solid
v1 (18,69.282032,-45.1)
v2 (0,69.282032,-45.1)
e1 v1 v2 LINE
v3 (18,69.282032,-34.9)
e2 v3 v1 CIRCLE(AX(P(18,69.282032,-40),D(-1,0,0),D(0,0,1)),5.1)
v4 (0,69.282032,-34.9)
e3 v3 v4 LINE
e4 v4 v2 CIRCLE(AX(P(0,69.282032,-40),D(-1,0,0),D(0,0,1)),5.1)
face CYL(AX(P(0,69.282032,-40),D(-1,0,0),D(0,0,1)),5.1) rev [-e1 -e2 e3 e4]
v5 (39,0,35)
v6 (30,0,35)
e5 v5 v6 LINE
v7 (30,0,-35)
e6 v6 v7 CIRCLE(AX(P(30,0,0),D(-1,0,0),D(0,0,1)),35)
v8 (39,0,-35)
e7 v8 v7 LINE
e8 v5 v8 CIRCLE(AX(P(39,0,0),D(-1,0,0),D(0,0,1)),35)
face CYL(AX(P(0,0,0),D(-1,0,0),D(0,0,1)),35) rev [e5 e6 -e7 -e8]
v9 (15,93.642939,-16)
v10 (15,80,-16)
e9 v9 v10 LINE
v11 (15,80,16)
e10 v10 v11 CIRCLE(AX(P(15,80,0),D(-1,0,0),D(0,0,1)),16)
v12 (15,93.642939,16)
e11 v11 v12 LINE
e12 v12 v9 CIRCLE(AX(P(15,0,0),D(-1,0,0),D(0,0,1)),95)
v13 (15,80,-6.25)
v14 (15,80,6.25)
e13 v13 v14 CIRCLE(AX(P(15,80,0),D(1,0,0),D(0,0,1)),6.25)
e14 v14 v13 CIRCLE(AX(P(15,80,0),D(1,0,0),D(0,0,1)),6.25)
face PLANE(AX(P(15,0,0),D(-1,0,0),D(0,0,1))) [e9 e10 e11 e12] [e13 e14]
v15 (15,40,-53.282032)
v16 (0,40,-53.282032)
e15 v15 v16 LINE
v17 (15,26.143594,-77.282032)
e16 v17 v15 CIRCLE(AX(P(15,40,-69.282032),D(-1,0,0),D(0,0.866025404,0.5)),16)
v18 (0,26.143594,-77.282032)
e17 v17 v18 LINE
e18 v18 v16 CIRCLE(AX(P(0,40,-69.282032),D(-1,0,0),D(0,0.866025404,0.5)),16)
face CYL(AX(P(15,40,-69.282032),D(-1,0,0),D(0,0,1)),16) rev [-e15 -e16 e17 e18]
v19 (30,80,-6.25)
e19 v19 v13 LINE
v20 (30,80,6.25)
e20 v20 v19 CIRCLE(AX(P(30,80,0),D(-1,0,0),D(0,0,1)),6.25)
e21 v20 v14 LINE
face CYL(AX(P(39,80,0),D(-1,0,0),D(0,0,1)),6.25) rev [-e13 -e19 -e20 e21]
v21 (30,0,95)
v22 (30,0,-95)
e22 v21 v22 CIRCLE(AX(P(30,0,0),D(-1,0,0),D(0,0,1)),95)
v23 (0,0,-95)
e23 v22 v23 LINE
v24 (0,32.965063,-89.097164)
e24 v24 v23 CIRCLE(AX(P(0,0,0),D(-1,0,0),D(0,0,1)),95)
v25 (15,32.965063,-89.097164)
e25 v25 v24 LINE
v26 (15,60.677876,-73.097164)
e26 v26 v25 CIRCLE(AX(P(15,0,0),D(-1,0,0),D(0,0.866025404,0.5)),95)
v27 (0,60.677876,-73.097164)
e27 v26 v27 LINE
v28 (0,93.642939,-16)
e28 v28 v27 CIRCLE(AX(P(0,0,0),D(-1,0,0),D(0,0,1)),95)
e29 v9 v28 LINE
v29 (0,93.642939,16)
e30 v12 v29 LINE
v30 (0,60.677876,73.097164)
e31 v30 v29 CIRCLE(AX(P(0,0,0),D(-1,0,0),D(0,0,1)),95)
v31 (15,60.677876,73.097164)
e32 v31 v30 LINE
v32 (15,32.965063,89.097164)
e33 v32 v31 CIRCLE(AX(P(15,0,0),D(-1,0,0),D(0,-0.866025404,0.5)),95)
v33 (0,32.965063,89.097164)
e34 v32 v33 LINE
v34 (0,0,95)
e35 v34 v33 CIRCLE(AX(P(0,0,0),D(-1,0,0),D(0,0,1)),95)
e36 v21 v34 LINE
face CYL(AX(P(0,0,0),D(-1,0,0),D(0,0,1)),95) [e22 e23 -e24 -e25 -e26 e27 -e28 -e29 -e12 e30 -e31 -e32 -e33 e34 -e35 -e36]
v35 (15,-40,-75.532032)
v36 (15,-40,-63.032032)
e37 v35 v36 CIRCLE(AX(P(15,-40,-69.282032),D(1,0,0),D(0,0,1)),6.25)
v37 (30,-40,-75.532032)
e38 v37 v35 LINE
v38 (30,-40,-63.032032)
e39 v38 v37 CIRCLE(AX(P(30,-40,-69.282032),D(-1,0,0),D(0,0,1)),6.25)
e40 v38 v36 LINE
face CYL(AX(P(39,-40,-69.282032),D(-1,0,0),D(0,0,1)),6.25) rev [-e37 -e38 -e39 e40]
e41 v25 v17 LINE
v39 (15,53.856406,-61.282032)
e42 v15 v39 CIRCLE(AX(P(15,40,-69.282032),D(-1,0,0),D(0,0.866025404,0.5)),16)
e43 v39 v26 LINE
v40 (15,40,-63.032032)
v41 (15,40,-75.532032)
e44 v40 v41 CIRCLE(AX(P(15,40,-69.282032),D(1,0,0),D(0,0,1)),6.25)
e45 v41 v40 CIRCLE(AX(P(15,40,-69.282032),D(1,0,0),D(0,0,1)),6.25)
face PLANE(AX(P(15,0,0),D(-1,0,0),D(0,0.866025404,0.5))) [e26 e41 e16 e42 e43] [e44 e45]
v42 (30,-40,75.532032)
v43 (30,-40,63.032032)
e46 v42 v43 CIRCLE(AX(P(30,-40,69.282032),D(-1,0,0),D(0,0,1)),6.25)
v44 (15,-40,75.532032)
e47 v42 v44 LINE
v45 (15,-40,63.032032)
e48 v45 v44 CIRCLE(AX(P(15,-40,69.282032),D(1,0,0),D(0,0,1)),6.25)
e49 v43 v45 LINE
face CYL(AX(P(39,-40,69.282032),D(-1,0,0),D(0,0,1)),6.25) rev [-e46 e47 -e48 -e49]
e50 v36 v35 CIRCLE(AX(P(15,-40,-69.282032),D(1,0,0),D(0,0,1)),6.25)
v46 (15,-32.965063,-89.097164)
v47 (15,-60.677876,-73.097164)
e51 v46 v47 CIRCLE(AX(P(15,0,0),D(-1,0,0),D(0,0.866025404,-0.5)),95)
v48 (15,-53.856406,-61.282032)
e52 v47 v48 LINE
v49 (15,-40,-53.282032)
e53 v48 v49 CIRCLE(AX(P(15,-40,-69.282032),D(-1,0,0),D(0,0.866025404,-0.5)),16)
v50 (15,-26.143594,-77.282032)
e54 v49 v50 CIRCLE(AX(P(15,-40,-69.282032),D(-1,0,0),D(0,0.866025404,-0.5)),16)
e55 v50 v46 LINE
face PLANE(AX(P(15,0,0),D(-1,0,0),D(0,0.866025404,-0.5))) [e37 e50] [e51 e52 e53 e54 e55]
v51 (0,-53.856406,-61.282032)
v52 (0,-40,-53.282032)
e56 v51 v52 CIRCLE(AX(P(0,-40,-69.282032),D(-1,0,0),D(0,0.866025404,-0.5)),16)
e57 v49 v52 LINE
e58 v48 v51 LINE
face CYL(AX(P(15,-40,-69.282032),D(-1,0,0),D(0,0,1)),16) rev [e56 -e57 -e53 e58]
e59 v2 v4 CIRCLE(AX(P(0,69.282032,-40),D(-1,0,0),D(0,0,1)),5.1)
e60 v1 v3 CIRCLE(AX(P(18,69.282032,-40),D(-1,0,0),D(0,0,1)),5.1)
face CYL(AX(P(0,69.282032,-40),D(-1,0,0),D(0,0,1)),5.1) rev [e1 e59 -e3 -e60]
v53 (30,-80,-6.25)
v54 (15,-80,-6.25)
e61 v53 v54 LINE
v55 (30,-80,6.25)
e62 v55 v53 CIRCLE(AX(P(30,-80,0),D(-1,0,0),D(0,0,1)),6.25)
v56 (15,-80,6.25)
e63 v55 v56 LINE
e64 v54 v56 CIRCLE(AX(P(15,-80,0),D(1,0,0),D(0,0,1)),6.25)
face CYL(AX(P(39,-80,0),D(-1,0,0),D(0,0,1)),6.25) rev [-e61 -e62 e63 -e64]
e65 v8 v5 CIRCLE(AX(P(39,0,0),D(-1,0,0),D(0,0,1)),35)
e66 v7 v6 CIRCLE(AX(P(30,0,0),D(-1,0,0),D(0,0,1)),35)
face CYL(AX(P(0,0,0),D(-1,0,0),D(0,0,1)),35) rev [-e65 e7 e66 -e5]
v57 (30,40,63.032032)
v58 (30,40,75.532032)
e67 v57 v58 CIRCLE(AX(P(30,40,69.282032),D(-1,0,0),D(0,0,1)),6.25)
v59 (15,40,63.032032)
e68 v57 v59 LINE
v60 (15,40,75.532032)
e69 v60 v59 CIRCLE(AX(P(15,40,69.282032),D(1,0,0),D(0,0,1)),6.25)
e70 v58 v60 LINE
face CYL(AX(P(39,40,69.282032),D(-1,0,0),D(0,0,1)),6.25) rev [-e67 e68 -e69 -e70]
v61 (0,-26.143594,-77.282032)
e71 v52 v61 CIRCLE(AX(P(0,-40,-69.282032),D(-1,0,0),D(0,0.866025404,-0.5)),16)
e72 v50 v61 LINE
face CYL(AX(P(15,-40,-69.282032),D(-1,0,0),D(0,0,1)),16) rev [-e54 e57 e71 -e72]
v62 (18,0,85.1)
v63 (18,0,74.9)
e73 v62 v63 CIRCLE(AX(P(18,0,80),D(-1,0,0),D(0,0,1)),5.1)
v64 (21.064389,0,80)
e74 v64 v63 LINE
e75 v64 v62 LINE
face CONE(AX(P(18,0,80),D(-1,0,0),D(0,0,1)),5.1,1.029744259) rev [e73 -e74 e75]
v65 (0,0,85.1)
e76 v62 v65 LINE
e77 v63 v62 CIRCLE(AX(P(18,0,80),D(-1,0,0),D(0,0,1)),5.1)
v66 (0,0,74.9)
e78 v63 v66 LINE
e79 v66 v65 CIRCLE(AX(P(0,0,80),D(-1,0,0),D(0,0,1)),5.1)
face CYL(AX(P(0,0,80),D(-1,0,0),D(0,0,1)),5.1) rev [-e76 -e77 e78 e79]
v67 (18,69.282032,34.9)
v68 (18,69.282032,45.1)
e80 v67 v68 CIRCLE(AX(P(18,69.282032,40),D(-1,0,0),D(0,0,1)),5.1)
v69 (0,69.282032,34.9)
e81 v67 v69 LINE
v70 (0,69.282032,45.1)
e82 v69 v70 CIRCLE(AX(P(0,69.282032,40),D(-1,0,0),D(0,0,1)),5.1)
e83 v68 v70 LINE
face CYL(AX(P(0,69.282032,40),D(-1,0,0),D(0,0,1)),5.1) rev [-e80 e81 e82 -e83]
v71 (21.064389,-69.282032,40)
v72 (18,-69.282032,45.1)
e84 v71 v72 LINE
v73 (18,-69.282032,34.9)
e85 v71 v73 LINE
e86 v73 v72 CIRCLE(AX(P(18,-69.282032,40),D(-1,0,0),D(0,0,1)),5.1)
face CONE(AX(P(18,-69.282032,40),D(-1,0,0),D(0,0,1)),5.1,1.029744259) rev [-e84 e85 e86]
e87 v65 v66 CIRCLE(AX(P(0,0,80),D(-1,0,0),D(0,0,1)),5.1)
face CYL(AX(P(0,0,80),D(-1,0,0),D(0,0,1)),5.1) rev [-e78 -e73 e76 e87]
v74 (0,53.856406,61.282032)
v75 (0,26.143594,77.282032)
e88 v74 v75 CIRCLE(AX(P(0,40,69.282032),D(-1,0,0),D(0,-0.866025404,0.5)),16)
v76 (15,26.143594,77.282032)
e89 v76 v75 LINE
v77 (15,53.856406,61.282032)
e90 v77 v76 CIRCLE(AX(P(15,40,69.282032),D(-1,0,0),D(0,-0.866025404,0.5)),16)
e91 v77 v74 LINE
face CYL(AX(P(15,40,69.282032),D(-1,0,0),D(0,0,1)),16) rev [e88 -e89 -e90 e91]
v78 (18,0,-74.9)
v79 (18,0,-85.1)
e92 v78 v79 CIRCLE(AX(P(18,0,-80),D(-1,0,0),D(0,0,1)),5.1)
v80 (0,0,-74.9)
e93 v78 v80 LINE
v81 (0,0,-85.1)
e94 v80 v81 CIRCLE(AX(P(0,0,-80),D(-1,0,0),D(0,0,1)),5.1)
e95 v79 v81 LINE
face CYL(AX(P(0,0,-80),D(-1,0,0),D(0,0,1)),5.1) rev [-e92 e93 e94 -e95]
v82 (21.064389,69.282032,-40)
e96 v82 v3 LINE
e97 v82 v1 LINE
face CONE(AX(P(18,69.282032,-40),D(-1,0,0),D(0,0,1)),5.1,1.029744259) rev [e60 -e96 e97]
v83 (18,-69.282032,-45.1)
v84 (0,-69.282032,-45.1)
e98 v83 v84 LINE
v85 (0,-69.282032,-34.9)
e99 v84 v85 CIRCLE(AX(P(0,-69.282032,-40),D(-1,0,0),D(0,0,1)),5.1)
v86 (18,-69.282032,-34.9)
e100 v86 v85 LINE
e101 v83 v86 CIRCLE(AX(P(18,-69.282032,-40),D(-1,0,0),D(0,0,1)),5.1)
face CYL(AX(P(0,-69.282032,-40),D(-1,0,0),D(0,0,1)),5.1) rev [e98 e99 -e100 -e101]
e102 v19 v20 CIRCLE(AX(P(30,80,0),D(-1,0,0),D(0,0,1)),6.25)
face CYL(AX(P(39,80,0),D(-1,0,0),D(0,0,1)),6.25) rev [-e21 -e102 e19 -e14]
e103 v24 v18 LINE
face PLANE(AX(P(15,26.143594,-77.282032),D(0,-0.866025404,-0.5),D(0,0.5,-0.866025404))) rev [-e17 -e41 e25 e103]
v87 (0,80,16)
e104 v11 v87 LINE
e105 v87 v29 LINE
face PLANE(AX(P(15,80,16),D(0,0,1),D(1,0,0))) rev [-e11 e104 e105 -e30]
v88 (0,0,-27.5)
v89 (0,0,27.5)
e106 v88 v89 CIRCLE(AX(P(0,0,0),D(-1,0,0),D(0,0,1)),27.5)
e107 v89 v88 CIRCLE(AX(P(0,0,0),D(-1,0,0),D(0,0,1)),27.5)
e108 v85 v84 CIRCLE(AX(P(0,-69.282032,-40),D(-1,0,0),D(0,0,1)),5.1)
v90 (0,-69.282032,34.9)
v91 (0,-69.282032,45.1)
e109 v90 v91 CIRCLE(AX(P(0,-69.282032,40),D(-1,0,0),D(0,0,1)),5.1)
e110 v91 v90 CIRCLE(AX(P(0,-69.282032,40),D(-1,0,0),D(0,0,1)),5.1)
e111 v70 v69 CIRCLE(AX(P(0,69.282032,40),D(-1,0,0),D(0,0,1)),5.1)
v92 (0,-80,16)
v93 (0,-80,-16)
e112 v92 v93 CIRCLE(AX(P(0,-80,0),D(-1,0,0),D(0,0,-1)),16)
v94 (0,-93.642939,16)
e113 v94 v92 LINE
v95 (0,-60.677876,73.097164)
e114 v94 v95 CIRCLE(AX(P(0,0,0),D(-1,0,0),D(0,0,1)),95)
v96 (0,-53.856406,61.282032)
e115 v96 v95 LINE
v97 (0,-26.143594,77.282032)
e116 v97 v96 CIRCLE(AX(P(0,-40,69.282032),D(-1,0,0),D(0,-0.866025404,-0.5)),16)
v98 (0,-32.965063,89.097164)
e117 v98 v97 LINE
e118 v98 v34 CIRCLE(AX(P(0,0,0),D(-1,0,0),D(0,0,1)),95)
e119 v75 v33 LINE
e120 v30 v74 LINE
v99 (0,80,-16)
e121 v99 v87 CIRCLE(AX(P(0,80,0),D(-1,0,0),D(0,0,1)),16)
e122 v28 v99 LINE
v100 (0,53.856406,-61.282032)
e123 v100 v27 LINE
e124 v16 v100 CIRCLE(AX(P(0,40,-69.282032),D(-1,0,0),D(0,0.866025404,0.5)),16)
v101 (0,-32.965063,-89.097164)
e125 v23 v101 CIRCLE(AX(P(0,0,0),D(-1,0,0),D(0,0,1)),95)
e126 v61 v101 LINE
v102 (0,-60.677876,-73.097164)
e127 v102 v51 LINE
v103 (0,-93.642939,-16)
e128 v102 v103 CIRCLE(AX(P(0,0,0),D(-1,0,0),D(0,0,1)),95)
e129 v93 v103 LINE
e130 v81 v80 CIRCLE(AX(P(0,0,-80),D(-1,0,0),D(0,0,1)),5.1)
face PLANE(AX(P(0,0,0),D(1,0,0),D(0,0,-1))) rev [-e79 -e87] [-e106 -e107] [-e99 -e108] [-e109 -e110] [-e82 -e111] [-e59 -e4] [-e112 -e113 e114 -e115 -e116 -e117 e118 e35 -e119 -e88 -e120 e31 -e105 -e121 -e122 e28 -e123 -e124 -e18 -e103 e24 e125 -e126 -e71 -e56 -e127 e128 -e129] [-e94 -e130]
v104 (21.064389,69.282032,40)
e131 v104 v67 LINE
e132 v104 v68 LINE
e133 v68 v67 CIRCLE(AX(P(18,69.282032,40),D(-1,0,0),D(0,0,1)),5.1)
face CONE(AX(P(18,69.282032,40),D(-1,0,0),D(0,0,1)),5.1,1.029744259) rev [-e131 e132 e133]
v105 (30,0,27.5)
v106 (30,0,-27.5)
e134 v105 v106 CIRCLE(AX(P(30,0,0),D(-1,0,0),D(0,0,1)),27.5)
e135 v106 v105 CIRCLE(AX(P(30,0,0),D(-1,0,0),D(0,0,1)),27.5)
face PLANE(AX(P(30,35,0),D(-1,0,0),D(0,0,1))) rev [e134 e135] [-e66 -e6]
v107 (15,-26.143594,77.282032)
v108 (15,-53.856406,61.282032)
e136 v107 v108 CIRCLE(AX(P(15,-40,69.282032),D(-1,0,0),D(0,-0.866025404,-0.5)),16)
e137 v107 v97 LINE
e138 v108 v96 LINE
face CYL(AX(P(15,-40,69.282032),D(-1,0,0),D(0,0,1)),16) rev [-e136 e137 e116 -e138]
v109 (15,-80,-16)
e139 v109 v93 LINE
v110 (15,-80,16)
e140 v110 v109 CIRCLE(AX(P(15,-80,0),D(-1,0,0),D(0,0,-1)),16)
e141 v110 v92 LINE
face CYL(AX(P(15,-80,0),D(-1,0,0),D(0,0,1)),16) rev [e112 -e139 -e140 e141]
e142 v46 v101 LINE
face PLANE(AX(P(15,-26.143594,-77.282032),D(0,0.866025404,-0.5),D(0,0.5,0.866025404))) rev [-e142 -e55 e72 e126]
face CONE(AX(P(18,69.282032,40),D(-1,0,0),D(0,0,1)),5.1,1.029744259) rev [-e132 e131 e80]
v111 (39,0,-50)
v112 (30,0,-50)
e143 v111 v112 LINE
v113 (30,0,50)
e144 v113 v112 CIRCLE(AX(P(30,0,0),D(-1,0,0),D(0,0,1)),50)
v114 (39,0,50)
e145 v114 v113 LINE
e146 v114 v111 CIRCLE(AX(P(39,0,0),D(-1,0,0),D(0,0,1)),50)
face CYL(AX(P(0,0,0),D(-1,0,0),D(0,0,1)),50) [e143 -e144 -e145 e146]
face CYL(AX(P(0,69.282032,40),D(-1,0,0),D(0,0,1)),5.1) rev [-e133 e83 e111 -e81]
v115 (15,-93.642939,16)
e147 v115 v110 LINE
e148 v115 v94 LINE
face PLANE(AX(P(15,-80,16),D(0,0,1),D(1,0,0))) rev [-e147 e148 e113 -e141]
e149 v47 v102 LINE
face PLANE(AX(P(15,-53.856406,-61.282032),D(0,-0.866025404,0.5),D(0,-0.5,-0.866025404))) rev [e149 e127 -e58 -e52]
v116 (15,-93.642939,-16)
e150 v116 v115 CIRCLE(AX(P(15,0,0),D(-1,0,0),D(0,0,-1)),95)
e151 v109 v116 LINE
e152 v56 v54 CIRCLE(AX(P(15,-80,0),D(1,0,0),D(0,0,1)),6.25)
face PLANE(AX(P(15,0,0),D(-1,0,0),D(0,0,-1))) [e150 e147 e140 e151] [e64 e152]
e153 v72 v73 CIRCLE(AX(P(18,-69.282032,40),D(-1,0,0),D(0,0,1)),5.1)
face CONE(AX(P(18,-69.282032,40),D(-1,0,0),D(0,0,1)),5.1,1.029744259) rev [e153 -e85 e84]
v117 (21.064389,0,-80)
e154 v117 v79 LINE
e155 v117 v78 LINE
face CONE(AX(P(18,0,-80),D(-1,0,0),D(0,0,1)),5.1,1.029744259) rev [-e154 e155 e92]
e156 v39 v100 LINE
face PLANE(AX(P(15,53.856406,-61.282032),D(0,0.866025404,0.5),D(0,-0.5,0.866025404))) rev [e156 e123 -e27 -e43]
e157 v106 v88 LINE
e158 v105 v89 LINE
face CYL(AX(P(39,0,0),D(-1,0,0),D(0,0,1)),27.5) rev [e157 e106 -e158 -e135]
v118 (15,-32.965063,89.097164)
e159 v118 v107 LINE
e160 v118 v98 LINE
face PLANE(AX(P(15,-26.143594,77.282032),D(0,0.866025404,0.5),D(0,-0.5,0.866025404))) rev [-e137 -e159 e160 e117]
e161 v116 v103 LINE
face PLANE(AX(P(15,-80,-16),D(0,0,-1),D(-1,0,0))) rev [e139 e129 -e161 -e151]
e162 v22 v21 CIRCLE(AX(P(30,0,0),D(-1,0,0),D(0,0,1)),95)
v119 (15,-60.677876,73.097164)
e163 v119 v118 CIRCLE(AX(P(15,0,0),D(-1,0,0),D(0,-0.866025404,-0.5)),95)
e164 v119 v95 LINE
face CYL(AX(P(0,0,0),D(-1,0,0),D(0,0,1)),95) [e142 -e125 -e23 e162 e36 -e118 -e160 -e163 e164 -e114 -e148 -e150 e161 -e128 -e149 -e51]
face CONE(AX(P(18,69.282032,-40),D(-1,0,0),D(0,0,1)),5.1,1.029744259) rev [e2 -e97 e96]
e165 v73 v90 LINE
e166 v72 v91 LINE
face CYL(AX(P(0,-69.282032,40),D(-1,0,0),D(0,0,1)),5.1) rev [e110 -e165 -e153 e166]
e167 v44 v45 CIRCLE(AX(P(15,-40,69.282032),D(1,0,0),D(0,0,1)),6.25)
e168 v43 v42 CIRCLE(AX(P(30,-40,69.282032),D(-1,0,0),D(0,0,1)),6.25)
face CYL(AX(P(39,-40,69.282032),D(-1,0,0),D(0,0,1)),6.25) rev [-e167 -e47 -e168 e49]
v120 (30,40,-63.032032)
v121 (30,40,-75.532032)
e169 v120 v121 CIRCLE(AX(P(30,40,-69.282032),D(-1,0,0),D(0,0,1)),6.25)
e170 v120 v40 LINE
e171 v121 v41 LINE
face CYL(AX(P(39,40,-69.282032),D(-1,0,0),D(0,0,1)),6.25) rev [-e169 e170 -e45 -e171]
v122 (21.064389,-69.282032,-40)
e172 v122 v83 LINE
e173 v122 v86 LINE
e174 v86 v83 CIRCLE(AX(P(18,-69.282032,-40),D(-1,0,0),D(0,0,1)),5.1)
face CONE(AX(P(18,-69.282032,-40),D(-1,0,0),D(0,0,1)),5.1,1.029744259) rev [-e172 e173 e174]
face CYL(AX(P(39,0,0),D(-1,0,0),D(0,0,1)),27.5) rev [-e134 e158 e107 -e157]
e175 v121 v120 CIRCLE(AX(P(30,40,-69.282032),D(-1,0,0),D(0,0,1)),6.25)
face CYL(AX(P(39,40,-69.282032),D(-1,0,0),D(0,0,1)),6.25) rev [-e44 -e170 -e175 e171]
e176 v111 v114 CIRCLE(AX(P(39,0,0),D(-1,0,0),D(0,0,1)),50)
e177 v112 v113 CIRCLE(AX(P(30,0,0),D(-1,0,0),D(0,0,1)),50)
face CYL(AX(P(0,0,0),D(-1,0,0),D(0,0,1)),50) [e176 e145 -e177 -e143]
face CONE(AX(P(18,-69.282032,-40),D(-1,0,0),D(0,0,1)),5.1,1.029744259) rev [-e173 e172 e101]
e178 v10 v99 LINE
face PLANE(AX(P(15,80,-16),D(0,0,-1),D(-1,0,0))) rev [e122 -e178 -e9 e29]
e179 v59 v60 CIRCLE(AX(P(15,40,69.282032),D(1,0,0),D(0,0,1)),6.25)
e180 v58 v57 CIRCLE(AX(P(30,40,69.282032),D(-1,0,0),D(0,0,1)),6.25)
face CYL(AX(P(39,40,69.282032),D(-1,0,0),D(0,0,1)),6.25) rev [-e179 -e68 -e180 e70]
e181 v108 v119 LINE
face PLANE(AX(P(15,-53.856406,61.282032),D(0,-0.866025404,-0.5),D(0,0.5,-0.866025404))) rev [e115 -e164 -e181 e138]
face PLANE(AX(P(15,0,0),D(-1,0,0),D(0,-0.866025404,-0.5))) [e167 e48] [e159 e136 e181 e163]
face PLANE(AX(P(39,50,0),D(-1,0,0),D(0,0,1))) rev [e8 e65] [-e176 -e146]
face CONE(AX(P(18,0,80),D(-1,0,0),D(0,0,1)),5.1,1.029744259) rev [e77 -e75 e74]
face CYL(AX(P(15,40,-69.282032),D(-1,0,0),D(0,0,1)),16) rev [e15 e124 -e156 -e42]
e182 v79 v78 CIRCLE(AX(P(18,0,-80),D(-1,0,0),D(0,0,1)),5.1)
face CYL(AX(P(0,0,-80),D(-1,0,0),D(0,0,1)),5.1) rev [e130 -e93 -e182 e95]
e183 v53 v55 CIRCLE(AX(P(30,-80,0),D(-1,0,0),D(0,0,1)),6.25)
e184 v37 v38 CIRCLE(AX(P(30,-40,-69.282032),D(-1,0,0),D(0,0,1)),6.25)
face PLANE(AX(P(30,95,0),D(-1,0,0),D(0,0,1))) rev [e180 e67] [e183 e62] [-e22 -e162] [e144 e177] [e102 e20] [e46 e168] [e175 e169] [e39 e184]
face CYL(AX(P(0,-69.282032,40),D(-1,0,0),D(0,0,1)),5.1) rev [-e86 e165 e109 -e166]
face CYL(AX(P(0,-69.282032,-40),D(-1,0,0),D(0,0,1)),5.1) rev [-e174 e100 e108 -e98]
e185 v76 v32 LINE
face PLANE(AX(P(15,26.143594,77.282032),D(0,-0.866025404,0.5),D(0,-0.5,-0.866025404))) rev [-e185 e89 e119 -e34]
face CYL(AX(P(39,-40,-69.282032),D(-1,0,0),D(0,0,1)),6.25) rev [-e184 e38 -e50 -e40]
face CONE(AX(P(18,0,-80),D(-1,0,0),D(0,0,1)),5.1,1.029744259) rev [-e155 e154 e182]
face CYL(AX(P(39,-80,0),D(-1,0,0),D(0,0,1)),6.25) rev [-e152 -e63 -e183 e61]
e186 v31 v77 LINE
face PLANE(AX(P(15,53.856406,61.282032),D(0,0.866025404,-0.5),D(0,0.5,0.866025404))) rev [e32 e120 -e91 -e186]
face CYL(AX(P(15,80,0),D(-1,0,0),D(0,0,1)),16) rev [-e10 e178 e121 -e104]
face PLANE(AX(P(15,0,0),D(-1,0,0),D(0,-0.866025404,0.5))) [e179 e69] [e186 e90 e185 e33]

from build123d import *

# Parameters (mm, degrees)
SKETCH_2_R               = 6.25
CUT_EXTRUDE_1_DEPTH      = 140.896390232
PATTERN_CIRCULAR_1_COUNT = 6
SKETCH_3_R               = 27.5
CUT_EXTRUDE_2_DEPTH      = 140.896390232
CUT_EXTRUDE_START        = -15
CUT_EXTRUDE_3_DEPTH      = 15
PATTERN_CIRCULAR_2_COUNT = 6
PATTERN_CIRCULAR_3_COUNT = 6


with BuildPart() as part:
    # 草图1 → 旋转1 (revolve)
    with BuildSketch(Plane.XY, mode=Mode.PRIVATE) as revolve_1_sk:
        Polygon((0, 0), (0, 95), (30, 95), (30, 50), (39, 50), (39, 35), (30, 35), (30, 0), align=None)
    revolve(revolve_1_sk.sketch.rotate(Axis((0, 0, 0), (1, 0, 0)), 90), axis=Axis((0, 0, 0), (1, 0, 0)))

    # 草图2 → 切除-拉伸1 (cut, through all)
    with BuildSketch(Plane.ZY):
        with Locations((0, 80)):
            Circle(SKETCH_2_R)
    cut_extrude_1 = extrude(amount=-CUT_EXTRUDE_1_DEPTH, mode=Mode.SUBTRACT)

    # 阵列(圆周)1: 切除-拉伸1 ×6 about axis
    pattern_circular_1_axis = Axis((0, 0, 0), (1, 0, 0))
    for i in range(1, PATTERN_CIRCULAR_1_COUNT):
        add(cut_extrude_1.rotate(pattern_circular_1_axis, i * 360 / PATTERN_CIRCULAR_1_COUNT), mode=Mode.SUBTRACT)

    # 草图3 → 切除-拉伸2 (cut, through all)
    with BuildSketch(Plane.ZY):
        Circle(SKETCH_3_R)
    extrude(amount=-CUT_EXTRUDE_2_DEPTH, mode=Mode.SUBTRACT)

    # 草图6 → 切除-拉伸3 (cut)
    with BuildSketch(Plane.ZY.offset(CUT_EXTRUDE_START)):
        with BuildLine():
            Line((-16, 80), (-16, 93.642938869))
            ThreePointArc((-16, 93.642938869), (0, 95), (16, 93.642938869))
            Line((16, 93.642938869), (16, 80))
            ThreePointArc((16, 80), (0, 64), (-16, 80))
        make_face()
    cut_extrude_3 = extrude(amount=CUT_EXTRUDE_3_DEPTH, mode=Mode.SUBTRACT)

    # 阵列(圆周)2: 切除-拉伸3 ×6 about axis
    pattern_circular_2_axis = Axis((0, 0, 0), (1, 0, 0))
    for i in range(1, PATTERN_CIRCULAR_2_COUNT):
        add(cut_extrude_3.rotate(pattern_circular_2_axis, i * 360 / PATTERN_CIRCULAR_2_COUNT), mode=Mode.SUBTRACT)

    # 草图8 → M12 螺纹孔1 (revolve, cut)
    with BuildSketch(Plane(origin=(0, 69.282032303, 40), x_dir=(0, 0, 1), z_dir=(0, 1, 0))):
        Polygon((0, 0), (0, 21.064389157), (5.1, 18), (5.1, 0), align=None)
    hole_wizard_m12_1 = revolve(axis=Axis((-6.35, 69.282032303, 40), (1, 0, 0)), mode=Mode.SUBTRACT)

    # 阵列(圆周)3: M12 螺纹孔1 ×6 about axis
    pattern_circular_3_axis = Axis((0, 0, 0), (1, 0, 0))
    for i in range(1, PATTERN_CIRCULAR_3_COUNT):
        add(hole_wizard_m12_1.rotate(pattern_circular_3_axis, i * 360 / PATTERN_CIRCULAR_3_COUNT), mode=Mode.SUBTRACT)


solid = part.part
